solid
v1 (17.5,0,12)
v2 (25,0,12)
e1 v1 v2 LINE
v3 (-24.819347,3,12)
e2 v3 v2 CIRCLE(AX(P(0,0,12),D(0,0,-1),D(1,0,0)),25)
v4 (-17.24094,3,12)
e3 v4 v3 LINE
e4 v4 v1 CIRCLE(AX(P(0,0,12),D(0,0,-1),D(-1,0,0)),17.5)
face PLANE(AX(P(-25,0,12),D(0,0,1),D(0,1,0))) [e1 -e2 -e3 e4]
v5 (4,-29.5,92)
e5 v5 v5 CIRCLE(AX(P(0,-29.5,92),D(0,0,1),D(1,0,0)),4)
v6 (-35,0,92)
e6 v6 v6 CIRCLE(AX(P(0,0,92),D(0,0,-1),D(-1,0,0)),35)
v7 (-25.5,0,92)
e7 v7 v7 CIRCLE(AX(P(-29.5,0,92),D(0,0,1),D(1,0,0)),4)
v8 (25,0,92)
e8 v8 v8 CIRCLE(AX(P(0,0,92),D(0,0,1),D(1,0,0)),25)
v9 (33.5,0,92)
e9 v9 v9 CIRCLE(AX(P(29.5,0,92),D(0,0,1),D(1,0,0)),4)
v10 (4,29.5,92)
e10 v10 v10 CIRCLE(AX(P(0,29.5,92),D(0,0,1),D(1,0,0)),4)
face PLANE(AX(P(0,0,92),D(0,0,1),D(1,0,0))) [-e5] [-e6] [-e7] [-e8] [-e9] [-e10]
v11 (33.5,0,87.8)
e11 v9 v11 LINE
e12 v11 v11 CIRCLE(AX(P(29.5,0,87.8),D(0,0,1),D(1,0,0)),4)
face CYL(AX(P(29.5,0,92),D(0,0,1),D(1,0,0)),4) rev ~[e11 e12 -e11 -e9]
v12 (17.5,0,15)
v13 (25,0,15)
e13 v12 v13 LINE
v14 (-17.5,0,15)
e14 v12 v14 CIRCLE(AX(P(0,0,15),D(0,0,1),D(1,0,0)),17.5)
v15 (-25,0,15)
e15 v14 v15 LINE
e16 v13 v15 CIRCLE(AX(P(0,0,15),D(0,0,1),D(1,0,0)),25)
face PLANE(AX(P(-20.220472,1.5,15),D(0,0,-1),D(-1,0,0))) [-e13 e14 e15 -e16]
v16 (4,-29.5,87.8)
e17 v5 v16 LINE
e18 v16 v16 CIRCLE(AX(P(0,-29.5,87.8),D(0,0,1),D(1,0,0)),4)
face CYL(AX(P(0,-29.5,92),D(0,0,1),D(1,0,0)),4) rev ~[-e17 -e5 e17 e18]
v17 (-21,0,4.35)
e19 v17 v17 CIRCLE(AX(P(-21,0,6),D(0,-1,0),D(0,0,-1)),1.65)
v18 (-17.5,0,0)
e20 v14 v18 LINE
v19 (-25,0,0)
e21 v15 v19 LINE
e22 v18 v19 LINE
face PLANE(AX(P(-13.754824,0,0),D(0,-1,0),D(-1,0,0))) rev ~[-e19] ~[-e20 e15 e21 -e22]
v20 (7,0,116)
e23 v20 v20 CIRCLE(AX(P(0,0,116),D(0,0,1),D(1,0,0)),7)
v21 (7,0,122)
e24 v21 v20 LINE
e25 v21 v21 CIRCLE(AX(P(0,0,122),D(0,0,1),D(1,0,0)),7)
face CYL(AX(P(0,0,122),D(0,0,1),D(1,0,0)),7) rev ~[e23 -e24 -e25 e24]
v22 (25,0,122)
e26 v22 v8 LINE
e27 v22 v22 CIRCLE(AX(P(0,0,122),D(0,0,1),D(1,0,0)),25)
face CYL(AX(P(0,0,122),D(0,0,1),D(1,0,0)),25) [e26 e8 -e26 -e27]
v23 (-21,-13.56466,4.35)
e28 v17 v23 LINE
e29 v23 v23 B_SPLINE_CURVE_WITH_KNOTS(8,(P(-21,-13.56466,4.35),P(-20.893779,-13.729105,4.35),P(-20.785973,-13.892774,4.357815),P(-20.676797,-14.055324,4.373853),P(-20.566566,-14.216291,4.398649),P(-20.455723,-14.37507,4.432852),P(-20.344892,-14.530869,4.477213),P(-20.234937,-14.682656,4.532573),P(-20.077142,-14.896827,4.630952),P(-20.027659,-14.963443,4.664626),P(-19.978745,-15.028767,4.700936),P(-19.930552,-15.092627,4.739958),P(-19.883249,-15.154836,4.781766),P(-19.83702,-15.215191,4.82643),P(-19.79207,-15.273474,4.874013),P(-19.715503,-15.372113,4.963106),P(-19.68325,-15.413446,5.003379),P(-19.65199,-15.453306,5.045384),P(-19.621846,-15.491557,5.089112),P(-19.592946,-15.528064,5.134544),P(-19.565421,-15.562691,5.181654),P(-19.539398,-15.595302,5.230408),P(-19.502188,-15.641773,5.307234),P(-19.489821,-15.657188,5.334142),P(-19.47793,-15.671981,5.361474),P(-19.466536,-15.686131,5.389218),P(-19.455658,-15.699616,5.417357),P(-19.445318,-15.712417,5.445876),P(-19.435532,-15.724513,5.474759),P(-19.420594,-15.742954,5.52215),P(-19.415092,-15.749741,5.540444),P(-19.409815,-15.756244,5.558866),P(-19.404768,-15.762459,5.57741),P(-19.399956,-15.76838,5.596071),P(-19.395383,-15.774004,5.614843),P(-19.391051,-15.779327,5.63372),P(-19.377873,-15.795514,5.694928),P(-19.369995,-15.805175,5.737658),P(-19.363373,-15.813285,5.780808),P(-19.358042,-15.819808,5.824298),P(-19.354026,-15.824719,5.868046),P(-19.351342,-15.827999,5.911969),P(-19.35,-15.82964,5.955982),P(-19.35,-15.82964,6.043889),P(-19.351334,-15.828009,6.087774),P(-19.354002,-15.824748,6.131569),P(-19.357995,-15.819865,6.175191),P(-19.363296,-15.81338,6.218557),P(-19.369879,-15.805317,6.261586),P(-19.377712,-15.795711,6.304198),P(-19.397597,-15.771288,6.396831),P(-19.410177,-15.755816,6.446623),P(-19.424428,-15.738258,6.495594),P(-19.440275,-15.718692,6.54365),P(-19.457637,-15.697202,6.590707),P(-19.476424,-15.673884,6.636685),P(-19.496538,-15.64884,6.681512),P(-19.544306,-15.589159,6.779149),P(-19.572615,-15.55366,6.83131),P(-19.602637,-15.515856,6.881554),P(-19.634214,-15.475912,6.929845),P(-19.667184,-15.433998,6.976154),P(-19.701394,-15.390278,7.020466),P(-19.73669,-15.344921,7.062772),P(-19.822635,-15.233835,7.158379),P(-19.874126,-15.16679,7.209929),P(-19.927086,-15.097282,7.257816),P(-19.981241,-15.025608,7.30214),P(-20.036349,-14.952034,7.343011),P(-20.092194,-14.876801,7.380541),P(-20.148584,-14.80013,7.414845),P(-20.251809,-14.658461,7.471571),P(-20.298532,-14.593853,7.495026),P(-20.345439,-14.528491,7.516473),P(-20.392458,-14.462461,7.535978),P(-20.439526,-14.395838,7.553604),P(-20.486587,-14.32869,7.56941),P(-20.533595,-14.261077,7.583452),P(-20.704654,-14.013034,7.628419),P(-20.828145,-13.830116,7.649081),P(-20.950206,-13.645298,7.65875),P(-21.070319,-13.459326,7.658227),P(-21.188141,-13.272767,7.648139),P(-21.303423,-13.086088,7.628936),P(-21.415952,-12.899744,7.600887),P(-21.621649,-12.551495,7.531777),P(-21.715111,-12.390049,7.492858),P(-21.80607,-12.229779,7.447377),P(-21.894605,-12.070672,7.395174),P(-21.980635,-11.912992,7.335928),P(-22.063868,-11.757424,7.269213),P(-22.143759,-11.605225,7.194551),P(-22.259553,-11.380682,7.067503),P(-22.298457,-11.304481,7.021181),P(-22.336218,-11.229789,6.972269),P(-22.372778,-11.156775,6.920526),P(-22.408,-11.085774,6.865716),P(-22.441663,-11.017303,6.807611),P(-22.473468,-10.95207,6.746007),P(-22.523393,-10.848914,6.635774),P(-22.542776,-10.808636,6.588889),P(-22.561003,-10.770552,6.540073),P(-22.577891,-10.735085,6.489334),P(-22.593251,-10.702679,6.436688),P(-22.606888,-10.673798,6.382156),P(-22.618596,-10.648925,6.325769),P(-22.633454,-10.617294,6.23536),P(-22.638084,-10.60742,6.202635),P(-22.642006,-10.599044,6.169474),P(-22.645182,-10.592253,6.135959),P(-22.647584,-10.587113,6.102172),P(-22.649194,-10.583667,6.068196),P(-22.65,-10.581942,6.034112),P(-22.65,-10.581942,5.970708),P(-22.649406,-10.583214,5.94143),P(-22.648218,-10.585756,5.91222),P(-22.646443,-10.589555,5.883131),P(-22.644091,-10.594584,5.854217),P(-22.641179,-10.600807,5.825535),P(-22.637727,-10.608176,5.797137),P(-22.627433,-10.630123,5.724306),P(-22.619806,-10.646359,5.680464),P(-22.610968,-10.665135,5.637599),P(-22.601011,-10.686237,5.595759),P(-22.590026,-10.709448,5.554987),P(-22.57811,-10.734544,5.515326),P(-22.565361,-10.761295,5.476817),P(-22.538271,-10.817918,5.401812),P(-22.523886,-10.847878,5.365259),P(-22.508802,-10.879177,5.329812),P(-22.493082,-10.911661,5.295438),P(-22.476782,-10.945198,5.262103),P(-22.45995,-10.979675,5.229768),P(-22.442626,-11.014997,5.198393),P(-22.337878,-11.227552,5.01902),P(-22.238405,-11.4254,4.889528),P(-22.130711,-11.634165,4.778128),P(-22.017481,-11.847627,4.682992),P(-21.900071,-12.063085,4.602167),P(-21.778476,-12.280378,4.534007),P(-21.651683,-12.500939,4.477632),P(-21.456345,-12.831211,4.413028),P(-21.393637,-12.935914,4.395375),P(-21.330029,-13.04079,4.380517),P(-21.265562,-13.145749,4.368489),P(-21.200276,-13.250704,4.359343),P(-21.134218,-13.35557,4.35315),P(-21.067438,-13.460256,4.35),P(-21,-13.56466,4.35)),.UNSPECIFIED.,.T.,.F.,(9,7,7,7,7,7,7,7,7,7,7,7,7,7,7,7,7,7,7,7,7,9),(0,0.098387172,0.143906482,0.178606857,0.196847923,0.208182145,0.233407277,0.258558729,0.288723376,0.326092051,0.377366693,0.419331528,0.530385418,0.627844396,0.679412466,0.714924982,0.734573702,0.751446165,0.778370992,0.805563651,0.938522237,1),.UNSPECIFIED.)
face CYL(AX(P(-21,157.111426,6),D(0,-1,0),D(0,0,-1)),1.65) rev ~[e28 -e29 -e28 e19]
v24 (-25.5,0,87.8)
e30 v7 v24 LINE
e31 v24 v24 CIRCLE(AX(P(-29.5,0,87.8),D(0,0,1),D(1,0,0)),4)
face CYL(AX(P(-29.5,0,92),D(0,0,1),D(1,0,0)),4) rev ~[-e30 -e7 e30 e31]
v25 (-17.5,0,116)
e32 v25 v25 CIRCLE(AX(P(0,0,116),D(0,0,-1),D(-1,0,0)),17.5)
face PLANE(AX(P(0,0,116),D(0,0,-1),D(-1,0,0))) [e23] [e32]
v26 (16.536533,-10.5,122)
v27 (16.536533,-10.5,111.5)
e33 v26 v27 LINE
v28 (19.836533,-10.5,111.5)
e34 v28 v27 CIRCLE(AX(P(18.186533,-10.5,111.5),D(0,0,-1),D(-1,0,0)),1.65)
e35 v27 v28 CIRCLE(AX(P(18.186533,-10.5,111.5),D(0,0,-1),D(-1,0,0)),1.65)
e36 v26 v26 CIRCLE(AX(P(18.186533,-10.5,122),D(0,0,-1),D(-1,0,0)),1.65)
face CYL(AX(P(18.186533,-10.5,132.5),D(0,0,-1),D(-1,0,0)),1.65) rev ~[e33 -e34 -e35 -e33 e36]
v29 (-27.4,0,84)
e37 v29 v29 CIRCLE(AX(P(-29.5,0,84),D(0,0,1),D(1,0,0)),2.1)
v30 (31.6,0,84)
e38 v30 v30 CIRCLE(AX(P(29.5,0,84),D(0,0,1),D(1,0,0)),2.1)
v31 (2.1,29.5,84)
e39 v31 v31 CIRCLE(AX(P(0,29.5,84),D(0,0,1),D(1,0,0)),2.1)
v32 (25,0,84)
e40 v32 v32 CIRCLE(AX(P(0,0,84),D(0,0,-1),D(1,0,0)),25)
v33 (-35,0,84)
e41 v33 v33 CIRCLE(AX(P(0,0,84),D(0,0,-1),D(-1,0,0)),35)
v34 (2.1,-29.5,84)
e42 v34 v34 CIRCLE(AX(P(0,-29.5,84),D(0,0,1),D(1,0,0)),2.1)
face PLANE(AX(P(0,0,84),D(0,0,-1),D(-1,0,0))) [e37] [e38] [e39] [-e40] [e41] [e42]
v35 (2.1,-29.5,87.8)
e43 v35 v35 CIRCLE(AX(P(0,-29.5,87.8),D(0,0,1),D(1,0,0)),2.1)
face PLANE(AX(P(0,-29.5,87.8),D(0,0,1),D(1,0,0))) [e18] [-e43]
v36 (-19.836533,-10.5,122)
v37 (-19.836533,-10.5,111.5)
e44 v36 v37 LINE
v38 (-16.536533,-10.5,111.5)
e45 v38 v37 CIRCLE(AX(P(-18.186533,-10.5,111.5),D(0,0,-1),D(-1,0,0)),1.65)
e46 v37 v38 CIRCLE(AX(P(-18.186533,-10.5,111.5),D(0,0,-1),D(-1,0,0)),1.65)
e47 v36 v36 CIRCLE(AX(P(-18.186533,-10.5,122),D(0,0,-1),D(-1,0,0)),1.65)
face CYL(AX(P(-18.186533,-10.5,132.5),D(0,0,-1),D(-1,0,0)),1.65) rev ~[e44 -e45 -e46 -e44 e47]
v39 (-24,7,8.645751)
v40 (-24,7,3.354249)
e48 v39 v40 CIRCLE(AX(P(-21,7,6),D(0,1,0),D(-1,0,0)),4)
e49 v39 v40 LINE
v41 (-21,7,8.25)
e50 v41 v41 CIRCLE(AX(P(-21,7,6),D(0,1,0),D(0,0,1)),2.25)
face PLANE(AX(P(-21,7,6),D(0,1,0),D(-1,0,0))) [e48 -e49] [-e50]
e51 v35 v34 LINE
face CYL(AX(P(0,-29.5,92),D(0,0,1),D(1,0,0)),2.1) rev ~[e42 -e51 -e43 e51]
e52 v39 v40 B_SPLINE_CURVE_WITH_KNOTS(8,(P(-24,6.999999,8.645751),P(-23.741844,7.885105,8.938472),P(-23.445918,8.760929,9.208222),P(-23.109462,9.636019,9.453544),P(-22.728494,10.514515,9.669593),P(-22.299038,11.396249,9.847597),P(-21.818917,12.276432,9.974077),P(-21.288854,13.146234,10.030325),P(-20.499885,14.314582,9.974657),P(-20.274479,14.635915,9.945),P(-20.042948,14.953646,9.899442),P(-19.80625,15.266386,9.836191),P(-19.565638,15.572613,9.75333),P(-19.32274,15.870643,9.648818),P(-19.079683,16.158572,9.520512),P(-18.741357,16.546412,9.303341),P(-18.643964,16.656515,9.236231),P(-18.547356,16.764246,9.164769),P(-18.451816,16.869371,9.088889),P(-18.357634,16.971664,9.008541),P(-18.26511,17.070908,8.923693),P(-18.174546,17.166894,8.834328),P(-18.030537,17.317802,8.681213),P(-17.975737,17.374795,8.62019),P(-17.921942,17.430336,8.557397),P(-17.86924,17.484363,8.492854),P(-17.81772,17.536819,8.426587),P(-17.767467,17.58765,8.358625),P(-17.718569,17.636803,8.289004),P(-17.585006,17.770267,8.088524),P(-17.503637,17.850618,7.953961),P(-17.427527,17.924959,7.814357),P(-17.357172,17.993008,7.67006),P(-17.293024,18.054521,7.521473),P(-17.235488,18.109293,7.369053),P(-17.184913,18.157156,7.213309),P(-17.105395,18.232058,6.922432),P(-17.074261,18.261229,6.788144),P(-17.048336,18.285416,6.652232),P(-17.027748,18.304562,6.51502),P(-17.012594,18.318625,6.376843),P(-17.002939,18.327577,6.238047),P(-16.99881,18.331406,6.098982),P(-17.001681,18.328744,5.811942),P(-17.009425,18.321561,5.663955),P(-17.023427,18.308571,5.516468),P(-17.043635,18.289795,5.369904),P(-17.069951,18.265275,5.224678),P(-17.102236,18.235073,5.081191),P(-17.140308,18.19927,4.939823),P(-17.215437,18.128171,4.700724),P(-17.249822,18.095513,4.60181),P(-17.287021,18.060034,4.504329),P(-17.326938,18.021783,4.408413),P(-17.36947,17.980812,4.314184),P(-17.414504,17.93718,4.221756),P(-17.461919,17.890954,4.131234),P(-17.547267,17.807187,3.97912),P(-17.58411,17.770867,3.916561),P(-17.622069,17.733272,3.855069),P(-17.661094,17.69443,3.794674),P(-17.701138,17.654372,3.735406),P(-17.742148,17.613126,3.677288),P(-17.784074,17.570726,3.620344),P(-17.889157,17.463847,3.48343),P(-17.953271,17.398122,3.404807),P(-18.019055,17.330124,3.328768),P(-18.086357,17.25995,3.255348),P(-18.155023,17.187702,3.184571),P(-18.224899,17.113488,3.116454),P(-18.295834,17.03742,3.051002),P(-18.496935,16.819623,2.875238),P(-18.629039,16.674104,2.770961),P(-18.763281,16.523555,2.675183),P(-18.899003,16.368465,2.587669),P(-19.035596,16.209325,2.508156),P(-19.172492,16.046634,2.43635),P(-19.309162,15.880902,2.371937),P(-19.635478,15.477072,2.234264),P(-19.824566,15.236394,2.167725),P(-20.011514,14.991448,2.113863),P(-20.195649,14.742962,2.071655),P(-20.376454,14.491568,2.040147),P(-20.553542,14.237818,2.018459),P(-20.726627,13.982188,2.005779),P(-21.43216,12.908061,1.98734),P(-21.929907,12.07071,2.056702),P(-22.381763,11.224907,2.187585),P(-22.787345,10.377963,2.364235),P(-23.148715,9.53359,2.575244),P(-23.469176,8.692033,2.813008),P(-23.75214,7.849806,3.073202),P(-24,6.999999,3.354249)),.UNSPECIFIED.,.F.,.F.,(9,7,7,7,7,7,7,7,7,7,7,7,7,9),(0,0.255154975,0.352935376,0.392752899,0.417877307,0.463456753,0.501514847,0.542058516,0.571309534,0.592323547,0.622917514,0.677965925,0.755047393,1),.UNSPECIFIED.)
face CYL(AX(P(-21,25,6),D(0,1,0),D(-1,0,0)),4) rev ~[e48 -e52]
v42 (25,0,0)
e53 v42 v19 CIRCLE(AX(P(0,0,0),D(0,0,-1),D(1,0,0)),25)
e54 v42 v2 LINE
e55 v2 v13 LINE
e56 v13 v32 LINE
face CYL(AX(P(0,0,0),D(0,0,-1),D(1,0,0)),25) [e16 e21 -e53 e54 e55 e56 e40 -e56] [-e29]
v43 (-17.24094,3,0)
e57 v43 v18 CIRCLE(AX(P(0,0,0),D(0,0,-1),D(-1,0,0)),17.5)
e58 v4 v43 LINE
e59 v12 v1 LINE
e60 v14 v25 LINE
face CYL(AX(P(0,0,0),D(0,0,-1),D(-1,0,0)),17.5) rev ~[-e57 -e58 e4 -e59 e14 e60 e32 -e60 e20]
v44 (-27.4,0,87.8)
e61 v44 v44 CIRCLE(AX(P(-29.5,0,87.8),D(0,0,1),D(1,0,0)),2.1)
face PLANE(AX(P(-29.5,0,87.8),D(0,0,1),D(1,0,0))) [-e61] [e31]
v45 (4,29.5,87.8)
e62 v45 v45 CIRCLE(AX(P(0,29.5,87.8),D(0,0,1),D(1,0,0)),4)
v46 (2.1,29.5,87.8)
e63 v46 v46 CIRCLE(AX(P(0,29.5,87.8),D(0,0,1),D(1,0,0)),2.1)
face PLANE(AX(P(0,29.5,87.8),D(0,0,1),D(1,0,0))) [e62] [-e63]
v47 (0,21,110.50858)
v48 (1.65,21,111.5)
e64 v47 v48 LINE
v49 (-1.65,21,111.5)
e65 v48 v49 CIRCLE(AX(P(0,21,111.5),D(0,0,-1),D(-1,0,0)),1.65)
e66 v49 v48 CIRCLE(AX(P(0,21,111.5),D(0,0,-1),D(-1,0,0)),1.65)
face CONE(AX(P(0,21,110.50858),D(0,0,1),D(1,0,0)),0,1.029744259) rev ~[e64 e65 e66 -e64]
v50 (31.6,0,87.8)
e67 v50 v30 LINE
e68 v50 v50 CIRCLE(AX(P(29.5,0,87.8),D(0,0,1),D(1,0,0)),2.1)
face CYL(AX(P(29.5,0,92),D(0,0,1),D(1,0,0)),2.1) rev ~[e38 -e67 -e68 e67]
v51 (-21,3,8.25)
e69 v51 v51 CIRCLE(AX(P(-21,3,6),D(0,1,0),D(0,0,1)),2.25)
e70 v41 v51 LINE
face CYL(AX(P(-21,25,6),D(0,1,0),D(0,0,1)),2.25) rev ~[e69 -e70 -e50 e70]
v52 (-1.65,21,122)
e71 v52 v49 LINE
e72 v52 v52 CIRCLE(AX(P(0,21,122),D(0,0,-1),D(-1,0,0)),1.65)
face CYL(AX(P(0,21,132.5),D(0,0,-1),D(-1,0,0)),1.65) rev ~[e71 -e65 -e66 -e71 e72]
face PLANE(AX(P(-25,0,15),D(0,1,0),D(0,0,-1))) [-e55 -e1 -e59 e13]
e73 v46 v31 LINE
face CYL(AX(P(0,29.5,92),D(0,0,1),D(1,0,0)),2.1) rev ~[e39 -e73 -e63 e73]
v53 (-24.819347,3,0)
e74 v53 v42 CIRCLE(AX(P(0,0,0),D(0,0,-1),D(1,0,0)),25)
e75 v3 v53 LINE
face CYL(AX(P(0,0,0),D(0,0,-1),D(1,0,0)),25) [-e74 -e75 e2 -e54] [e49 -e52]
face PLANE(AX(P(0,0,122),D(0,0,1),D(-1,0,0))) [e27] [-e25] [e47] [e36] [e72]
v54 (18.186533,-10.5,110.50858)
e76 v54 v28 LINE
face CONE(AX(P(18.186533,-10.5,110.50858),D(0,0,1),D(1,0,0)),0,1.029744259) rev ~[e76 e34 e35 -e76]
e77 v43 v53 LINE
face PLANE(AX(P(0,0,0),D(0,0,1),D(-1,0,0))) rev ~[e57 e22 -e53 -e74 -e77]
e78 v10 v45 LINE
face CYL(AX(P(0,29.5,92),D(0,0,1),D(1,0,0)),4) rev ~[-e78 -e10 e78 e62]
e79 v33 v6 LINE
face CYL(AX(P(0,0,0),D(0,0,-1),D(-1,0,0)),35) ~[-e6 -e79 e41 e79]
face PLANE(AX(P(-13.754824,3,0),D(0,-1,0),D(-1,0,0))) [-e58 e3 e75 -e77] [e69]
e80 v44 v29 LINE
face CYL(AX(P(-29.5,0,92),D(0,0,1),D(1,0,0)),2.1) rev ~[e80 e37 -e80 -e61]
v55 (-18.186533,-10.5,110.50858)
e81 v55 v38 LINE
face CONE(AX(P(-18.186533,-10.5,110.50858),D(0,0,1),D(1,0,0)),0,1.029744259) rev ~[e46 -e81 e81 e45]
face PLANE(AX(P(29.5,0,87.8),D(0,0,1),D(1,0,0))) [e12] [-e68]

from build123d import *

# Parameters (mm, degrees)
SKETCH_2_R             = 35
EXTRUDE_1_DEPTH        = 122
SKETCH_3_R             = 7
CUT_EXTRUDE_1_DEPTH    = 132.658649545
SKETCH_4_R             = 17.5
CUT_EXTRUDE_2_DEPTH    = 116
SKETCH_5_OUTSIDE_W     = 103.422
SKETCH_5_OUTSIDE_H     = 103.422
SKETCH_5_OUTSIDE_R     = 25
CUT_EXTRUDE_3_DEPTH    = 30
SKETCH_6_OUTSIDE_W     = 103.422
SKETCH_6_OUTSIDE_H     = 103.422
SKETCH_6_OUTSIDE_R     = 25
CUT_EXTRUDE_4_DEPTH    = 84
SKETCH_7_R             = 2.1
CUT_EXTRUDE_5_DEPTH    = 105.470091414
SKETCH_8_R             = 4
CUT_EXTRUDE_6_DEPTH    = 4.2
HOLE_WIZARD_M4_1_D     = 3.3
HOLE_WIZARD_M4_1_DEPTH = 10.5
HOLE_WIZARD_M4_1_TIP   = 0.991420021
SKETCH_19_W            = 12.931297241
SKETCH_19_H            = 3
CUT_EXTRUDE_7_DEPTH    = 15
SKETCH_20_W            = 3
SKETCH_20_H            = 28.427665472
CUT_EXTRUDE_8_DEPTH    = 141.388745988
SKETCH_21_R            = 4
CUT_EXTRUDE_9_DEPTH    = 18
SKETCH_22_R            = 2.25
CUT_EXTRUDE_10_DEPTH   = 22
HOLE_WIZARD_M4_3_D     = 3.3


with BuildPart() as part:
    # 草图2 → 凸台-拉伸1 (new body)
    with BuildSketch(Plane.XY):
        with Locations(Location((0, 0, 0), (0, 0, 180))):
            Circle(SKETCH_2_R)
    extrude(amount=EXTRUDE_1_DEPTH)

    # 草图3 → 切除-拉伸1 (cut, through all)
    with BuildSketch(Plane.XY.offset(122)):
        Circle(SKETCH_3_R)
    extrude(amount=-CUT_EXTRUDE_1_DEPTH, mode=Mode.SUBTRACT)

    # 草图4 → 切除-拉伸2 (cut)
    with BuildSketch(Plane(origin=(0, 0, 0), x_dir=(-1, 0, 0), z_dir=(0, 0, -1))):
        Circle(SKETCH_4_R)
    extrude(amount=-CUT_EXTRUDE_2_DEPTH, mode=Mode.SUBTRACT)

    # 草图5 outside → 切除-拉伸3 (cut)
    with BuildSketch(Plane.XY.offset(122)):
        Rectangle(SKETCH_5_OUTSIDE_W, SKETCH_5_OUTSIDE_H)
        Circle(SKETCH_5_OUTSIDE_R, mode=Mode.SUBTRACT)
    extrude(amount=-CUT_EXTRUDE_3_DEPTH, mode=Mode.SUBTRACT)

    # 草图6 outside → 切除-拉伸4 (cut)
    with BuildSketch(Plane(origin=(0, 0, 0), x_dir=(-1, 0, 0), z_dir=(0, 0, -1))):
        Rectangle(SKETCH_6_OUTSIDE_W, SKETCH_6_OUTSIDE_H)
        with Locations(Location((0, 0, 0), (0, 0, 180))):
            Circle(SKETCH_6_OUTSIDE_R, mode=Mode.SUBTRACT)
    extrude(amount=-CUT_EXTRUDE_4_DEPTH, mode=Mode.SUBTRACT)

    # 草图7 → 切除-拉伸5 (cut, through all)
    with BuildSketch(Plane.XY.offset(92)):
        with Locations((0, 29.5)):
            Circle(SKETCH_7_R)
        with Locations((29.5, 0)):
            Circle(SKETCH_7_R)
        with Locations((0, -29.5)):
            Circle(SKETCH_7_R)
        with Locations((-29.5, 0)):
            Circle(SKETCH_7_R)
    extrude(amount=-CUT_EXTRUDE_5_DEPTH, mode=Mode.SUBTRACT)

    # 草图8 → 切除-拉伸6 (cut)
    with BuildSketch(Plane.XY.offset(92)):
        with Locations((0, 29.5)):
            Circle(SKETCH_8_R)
        with Locations((-29.5, 0)):
            Circle(SKETCH_8_R)
        with Locations((29.5, 0)):
            Circle(SKETCH_8_R)
        with Locations((0, -29.5)):
            Circle(SKETCH_8_R)
    extrude(amount=-CUT_EXTRUDE_6_DEPTH, mode=Mode.SUBTRACT)

    # M4 螺纹孔1
    with Locations(Plane(origin=(18.186533479, -10.5, 122), x_dir=(1, 0, 0), z_dir=(0, 0, 1))):
        with Locations((0, 0), (-36.373066958, 0), (-18.186533479, 31.5)):
            Hole(HOLE_WIZARD_M4_1_D / 2, depth=HOLE_WIZARD_M4_1_DEPTH)
            with Locations((0, 0, -(HOLE_WIZARD_M4_1_DEPTH + HOLE_WIZARD_M4_1_TIP / 2))):  # 118° drill point
                Cone(0, HOLE_WIZARD_M4_1_D / 2, HOLE_WIZARD_M4_1_TIP, mode=Mode.SUBTRACT)

    # 草图19 → 切除-拉伸7 (cut)
    with BuildSketch(Plane(origin=(0, 0, 0), x_dir=(-1, 0, 0), z_dir=(0, 0, -1))):
        with Locations((20.220472236, 1.5)):
            Rectangle(SKETCH_19_W, SKETCH_19_H)
    extrude(amount=-CUT_EXTRUDE_7_DEPTH, mode=Mode.SUBTRACT)

    # 草图20 → 切除-拉伸8 (cut, through all)
    with BuildSketch(Plane(origin=(-25, 0, 0), x_dir=(0, 0, -1), z_dir=(1, 0, 0))):
        with Locations((-13.5, 14.213832736)):
            Rectangle(SKETCH_20_W, SKETCH_20_H)
    extrude(amount=CUT_EXTRUDE_8_DEPTH, mode=Mode.SUBTRACT)

    # 草图21 → 切除-拉伸9 (cut)
    with BuildSketch(Plane(origin=(0, 25, 0), x_dir=(-1, 0, 0), z_dir=(0, 1, 0))):
        with Locations((21, 6)):
            Circle(SKETCH_21_R)
    extrude(amount=-CUT_EXTRUDE_9_DEPTH, mode=Mode.SUBTRACT)

    # 草图22 → 切除-拉伸10 (cut)
    with BuildSketch(Plane(origin=(0, 25, 0), x_dir=(-1, 0, 0), z_dir=(0, 1, 0))):
        with Locations(Location((21, 6, 0), (0, 0, 90))):
            Circle(SKETCH_22_R)
    extrude(amount=-CUT_EXTRUDE_10_DEPTH, mode=Mode.SUBTRACT)

    # M4 螺纹孔3 (through all)
    with Locations(Plane(origin=(-21, 0, 6), x_dir=(0, 0, 1), z_dir=(0, 1, 0))):
        with Locations((0, 0)):
            Hole(HOLE_WIZARD_M4_3_D / 2)


solid = part.part
